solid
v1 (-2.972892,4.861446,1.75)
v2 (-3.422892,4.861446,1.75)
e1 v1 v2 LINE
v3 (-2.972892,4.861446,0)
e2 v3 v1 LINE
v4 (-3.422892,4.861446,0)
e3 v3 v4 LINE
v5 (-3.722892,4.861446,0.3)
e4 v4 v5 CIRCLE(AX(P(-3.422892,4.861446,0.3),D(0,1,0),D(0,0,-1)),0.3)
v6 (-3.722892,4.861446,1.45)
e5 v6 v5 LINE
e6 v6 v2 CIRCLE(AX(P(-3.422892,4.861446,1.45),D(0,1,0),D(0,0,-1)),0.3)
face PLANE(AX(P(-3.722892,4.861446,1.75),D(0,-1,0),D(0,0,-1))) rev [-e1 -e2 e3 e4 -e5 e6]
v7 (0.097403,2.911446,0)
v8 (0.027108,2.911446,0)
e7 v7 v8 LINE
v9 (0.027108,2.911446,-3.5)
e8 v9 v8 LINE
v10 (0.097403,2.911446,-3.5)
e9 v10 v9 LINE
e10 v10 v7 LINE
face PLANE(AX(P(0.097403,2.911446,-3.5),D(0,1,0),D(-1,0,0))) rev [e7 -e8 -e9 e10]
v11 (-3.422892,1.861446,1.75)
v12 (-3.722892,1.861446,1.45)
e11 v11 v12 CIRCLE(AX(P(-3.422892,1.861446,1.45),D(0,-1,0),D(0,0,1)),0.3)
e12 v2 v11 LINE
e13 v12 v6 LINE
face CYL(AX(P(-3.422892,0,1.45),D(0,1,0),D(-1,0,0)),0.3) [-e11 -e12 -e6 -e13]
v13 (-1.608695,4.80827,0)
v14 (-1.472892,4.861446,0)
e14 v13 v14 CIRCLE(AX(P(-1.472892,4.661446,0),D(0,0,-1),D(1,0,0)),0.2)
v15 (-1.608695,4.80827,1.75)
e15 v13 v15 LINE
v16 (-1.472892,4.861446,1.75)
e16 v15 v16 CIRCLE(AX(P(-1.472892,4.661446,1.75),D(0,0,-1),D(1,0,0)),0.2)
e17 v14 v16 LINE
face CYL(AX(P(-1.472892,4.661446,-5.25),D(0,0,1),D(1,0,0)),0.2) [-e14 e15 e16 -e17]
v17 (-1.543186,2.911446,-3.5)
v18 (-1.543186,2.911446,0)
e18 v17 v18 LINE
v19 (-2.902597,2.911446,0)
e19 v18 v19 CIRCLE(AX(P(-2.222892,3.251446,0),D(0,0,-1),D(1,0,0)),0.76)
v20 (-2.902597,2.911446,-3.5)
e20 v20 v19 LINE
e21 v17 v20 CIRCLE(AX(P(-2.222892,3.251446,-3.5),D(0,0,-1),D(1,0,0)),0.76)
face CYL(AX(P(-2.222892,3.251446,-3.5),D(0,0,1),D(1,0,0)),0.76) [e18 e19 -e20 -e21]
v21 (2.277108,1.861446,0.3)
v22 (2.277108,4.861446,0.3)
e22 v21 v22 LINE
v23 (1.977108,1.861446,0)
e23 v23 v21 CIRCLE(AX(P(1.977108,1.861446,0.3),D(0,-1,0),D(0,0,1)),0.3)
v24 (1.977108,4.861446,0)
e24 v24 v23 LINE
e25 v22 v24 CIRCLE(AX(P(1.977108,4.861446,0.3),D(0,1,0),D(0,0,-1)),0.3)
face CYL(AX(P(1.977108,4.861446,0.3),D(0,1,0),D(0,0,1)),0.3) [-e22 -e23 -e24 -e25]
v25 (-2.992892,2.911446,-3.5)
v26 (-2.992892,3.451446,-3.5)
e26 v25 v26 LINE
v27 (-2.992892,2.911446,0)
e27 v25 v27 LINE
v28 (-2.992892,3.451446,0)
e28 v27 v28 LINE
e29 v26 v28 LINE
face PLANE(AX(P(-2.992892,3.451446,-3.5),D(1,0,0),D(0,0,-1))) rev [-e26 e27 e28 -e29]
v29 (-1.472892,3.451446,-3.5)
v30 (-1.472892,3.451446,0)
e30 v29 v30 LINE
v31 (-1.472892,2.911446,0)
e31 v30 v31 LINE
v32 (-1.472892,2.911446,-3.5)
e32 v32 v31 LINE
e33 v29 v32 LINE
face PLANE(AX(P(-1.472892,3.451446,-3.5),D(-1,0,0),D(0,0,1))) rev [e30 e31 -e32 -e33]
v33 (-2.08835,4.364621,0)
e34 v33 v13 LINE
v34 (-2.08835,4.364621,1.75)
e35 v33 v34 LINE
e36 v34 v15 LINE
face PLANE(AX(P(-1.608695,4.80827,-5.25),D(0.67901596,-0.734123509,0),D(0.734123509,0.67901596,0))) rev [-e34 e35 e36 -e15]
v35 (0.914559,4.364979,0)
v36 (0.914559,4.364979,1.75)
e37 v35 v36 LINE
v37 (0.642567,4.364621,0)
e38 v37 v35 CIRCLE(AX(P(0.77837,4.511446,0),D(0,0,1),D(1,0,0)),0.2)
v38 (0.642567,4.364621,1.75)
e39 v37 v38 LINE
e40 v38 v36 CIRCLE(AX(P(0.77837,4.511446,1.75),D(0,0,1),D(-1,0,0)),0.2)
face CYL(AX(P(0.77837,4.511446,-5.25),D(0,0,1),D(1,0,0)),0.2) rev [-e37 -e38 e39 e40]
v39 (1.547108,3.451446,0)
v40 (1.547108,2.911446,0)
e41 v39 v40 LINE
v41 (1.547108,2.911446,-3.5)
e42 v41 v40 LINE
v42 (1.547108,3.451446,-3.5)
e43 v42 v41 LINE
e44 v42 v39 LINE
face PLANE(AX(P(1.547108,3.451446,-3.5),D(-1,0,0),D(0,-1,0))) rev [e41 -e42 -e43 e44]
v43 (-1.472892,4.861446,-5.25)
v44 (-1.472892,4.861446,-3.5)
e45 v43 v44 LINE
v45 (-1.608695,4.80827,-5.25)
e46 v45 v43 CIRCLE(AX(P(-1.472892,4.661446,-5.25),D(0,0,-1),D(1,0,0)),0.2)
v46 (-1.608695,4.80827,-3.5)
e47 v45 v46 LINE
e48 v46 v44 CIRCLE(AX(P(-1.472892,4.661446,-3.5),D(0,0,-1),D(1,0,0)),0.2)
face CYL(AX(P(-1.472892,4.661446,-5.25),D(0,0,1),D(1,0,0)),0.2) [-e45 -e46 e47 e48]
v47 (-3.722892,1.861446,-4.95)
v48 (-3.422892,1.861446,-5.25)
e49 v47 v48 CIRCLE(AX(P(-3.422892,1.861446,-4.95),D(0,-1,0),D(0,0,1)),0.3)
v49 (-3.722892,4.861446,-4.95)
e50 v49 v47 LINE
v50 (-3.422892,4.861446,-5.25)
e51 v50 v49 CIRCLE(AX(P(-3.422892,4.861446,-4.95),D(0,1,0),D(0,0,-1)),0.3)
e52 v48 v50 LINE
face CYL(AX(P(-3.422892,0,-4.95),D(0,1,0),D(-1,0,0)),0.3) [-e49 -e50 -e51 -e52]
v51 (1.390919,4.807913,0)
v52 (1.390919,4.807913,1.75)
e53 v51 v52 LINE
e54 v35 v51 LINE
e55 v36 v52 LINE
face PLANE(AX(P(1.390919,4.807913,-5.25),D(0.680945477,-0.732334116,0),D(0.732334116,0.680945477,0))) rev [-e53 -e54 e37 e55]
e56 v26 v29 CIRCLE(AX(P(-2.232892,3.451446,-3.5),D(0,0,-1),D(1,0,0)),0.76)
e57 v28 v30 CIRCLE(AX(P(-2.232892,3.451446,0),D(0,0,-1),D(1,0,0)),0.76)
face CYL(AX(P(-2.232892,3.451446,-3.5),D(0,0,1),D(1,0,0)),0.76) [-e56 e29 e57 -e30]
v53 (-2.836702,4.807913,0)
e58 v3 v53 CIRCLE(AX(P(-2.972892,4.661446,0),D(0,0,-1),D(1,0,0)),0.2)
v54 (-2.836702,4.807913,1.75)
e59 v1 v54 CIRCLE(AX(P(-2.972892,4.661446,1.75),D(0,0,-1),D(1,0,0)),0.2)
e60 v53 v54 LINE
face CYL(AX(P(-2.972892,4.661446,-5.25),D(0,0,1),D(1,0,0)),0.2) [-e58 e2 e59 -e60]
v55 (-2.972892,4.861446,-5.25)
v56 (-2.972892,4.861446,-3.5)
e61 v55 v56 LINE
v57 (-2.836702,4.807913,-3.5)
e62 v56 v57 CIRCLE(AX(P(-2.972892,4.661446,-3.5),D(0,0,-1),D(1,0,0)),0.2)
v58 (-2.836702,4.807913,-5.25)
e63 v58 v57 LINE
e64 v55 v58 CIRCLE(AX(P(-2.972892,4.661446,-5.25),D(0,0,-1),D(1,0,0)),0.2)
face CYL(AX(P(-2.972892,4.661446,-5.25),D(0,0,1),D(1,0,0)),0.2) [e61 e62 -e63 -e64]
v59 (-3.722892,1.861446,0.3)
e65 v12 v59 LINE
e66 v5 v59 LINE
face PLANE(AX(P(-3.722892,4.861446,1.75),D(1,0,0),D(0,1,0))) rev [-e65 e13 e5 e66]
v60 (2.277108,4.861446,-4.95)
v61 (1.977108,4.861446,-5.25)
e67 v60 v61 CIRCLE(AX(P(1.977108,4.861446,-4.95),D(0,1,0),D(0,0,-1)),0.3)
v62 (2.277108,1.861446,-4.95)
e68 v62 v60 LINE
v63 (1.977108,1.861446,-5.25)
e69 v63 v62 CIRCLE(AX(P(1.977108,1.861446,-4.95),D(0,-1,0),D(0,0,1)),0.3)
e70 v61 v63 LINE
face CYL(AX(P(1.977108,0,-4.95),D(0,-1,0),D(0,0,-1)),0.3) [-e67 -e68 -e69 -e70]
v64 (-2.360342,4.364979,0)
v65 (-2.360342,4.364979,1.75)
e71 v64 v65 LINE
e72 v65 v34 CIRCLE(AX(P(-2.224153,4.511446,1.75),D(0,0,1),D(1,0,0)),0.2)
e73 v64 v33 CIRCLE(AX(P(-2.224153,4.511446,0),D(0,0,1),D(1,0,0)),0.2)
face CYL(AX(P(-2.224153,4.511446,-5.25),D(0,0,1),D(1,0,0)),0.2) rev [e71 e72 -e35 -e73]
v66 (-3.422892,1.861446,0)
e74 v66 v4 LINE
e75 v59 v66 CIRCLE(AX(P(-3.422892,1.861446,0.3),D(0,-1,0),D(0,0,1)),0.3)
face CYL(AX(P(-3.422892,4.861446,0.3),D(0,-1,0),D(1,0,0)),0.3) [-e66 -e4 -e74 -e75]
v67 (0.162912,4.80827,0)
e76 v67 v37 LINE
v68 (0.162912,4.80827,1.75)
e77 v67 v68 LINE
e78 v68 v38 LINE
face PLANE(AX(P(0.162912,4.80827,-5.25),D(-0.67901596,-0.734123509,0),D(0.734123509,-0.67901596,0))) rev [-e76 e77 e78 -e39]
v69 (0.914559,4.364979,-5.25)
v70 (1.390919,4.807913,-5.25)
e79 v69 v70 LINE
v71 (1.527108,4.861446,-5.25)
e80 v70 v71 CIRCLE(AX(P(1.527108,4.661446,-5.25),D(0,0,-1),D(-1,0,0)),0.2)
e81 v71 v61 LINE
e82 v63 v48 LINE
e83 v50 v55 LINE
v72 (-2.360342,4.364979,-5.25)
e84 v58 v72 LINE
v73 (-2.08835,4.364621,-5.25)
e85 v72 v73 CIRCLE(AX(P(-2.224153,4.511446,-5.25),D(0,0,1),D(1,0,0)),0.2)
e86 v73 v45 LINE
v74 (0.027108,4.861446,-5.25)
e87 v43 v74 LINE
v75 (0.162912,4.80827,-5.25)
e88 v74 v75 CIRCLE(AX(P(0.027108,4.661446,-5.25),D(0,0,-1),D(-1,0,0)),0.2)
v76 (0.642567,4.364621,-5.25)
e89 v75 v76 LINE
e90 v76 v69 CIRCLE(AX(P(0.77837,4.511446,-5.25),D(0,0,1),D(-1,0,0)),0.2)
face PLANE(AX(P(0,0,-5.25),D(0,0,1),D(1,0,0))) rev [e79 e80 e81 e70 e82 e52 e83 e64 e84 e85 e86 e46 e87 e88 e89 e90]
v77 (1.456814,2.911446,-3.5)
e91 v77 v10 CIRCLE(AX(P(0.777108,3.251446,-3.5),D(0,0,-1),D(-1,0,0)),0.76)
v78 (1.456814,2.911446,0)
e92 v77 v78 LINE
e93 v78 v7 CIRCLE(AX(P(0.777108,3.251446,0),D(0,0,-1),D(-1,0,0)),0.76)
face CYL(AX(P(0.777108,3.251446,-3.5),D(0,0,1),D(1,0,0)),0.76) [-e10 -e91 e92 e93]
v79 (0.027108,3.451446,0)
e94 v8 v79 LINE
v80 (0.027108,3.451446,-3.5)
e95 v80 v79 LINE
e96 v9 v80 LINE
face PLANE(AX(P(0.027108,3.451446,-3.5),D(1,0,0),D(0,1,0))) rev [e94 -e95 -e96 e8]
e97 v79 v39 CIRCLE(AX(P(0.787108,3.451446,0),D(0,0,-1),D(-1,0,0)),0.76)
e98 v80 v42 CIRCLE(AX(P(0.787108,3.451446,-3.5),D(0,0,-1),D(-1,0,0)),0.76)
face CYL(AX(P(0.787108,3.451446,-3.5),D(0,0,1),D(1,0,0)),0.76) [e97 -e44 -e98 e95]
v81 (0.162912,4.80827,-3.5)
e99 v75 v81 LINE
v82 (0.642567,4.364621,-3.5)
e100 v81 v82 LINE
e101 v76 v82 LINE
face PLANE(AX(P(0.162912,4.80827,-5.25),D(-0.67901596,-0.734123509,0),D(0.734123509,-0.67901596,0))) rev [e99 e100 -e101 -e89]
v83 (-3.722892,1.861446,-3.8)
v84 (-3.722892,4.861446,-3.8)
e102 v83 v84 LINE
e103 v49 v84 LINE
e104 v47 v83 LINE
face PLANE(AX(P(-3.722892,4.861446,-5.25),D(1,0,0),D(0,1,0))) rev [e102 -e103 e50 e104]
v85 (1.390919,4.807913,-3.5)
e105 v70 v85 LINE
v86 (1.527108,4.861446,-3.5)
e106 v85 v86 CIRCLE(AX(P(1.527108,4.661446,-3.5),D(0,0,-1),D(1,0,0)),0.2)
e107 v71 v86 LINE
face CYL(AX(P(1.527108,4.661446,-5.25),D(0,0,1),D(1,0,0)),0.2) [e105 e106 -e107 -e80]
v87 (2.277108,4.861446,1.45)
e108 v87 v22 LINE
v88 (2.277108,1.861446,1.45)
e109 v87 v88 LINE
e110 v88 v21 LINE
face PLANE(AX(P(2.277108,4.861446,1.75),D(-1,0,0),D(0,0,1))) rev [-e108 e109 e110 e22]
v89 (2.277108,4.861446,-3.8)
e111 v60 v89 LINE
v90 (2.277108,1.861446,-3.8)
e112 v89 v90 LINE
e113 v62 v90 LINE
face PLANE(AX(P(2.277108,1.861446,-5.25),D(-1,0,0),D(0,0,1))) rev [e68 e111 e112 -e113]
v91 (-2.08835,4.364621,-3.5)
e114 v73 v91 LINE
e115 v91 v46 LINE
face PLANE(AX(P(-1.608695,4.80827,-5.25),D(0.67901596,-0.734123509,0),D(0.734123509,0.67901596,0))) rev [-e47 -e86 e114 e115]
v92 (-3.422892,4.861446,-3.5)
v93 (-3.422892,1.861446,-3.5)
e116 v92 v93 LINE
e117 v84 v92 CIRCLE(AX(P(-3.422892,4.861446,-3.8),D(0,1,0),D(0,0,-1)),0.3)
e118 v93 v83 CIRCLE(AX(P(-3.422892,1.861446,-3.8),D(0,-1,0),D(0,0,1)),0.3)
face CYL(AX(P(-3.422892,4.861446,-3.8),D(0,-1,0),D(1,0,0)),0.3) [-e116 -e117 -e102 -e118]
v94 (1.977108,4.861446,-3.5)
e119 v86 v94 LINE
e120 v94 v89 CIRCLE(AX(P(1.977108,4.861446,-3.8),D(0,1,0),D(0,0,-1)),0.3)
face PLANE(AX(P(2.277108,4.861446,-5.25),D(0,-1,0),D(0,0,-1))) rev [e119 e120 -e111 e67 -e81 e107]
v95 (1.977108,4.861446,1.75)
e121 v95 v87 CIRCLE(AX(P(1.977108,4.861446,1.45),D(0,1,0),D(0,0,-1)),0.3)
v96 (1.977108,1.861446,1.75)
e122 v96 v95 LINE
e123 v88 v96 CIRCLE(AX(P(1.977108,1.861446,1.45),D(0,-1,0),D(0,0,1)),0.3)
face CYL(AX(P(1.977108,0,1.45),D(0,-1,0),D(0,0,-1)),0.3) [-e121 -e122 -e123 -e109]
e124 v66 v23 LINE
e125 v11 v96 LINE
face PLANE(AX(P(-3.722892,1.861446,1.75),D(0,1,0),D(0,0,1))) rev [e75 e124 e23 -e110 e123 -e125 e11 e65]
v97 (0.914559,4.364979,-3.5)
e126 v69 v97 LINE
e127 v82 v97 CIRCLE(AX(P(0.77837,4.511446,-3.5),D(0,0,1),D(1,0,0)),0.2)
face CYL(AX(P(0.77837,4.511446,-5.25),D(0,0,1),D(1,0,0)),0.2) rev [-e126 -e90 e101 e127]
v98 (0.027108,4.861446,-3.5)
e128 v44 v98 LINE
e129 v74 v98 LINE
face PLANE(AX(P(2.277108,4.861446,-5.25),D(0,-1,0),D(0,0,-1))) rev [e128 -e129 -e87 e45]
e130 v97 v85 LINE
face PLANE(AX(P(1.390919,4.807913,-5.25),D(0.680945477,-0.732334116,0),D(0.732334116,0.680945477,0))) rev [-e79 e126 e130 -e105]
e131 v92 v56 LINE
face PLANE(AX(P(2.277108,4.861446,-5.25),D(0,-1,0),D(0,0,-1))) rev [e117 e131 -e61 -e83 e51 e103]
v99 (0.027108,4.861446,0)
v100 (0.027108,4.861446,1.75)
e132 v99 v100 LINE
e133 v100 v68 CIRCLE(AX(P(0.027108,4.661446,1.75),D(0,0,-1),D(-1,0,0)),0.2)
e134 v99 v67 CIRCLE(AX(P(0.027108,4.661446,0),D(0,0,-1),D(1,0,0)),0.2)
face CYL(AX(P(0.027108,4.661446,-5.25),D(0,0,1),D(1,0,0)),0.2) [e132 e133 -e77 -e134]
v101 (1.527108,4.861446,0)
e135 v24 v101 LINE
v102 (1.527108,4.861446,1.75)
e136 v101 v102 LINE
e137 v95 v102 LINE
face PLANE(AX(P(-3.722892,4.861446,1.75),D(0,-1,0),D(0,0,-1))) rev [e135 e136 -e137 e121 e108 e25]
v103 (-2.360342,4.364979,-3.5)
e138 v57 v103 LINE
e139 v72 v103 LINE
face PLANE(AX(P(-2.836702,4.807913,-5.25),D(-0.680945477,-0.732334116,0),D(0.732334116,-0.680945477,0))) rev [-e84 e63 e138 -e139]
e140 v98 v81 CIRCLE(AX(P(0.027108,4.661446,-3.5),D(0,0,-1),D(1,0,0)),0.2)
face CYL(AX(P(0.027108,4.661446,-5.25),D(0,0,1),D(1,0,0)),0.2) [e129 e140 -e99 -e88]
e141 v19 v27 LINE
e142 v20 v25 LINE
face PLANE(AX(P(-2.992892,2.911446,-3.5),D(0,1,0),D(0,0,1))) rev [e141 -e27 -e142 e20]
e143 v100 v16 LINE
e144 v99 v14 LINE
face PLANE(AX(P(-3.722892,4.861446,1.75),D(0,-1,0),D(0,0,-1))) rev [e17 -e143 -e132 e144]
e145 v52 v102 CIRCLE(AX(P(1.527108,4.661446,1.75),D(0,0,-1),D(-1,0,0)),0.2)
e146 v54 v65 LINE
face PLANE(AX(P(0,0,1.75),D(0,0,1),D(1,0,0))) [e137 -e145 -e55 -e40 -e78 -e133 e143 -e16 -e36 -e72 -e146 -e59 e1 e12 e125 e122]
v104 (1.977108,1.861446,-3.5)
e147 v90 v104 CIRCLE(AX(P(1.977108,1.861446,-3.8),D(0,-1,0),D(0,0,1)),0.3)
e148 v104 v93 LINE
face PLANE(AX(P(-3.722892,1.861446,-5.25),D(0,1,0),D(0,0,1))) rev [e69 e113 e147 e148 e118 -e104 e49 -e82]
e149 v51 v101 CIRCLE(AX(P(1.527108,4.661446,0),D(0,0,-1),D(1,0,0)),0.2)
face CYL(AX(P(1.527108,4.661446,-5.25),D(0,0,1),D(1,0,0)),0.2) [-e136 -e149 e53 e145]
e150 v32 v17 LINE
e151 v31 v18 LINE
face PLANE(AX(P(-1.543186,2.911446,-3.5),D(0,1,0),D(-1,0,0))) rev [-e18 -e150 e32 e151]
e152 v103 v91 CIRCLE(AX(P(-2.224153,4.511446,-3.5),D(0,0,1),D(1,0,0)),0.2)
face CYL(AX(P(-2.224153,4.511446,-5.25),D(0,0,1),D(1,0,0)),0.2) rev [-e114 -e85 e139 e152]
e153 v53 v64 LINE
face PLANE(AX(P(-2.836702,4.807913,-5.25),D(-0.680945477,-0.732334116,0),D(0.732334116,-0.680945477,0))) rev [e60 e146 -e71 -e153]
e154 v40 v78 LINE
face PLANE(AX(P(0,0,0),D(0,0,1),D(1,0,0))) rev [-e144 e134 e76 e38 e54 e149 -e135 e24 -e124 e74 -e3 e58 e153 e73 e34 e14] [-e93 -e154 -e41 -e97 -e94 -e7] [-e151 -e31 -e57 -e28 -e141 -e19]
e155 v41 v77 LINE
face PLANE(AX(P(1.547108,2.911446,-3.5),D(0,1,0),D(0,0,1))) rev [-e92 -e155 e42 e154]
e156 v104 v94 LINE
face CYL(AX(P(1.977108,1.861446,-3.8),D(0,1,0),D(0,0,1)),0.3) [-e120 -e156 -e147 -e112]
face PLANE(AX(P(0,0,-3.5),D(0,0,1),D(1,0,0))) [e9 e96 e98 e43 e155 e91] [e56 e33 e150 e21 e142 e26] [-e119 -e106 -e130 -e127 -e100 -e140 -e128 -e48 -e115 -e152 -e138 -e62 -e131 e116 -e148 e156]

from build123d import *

# Parameters (mm, degrees)
SKETCH_1_W          = 6
SKETCH_1_H          = 3
EXTRUDE_1_DEPTH     = 1.75
EXTRUDE_2_DEPTH     = 3.5
FILLET_5_R          = 0.3
FILLET_6_R          = 0.3
FILLET_7_R          = 0.3
FILLET_8_R          = 0.3
SKETCH_6_W          = 6
SKETCH_6_H          = 3
EXTRUDE_4_DEPTH     = 1.75
FILLET_9_R          = 0.3
FILLET_10_R         = 0.3
FILLET_11_R         = 0.3
FILLET_12_R         = 0.3
CUT_EXTRUDE_1_DEPTH = 10.300192295


with BuildPart() as part:
    # 草图1 → 凸台-拉伸1 (new body)
    with BuildSketch(Plane.XY):
        with Locations((-0.722891566, 3.361445783)):
            Rectangle(SKETCH_1_W, SKETCH_1_H)
    extrude(amount=EXTRUDE_1_DEPTH)

    # 草图2 → 凸台-拉伸2 (add)
    with BuildSketch(Plane(origin=(0, 0, 0), x_dir=(-1, 0, 0), z_dir=(0, 0, -1))):
        with BuildLine():
            Line((-0.097402615, 2.911445783), (-0.027108434, 2.911445783))
            Line((-0.027108434, 2.911445783), (-0.027108434, 3.451445783))
            ThreePointArc((-0.027108434, 3.451445783), (-0.787108434, 4.211445783), (-1.547108434, 3.451445783))
            Line((-1.547108434, 3.451445783), (-1.547108434, 2.911445783))
            Line((-1.547108434, 2.911445783), (-1.456814252, 2.911445783))
            ThreePointArc((-1.456814252, 2.911445783), (-0.777108434, 2.491445783), (-0.097402615, 2.911445783))
        make_face()
        with BuildLine():
            Line((1.472891566, 3.451445783), (1.472891566, 2.911445783))
            Line((1.472891566, 2.911445783), (1.543185748, 2.911445783))
            ThreePointArc((1.543185748, 2.911445783), (2.222891566, 2.491445783), (2.902597385, 2.911445783))
            Line((2.902597385, 2.911445783), (2.992891566, 2.911445783))
            Line((2.992891566, 2.911445783), (2.992891566, 3.451445783))
            ThreePointArc((2.992891566, 3.451445783), (2.232891566, 4.211445783), (1.472891566, 3.451445783))
        make_face()
    extrude(amount=EXTRUDE_2_DEPTH)

    # 圆角5
    fillet_5_edges = [part.edges().sort_by_distance(p)[0] for p in [
        (2.277108434, 3.361445783, 1.75),
    ]]
    fillet(fillet_5_edges, radius=FILLET_5_R)

    # 圆角6
    fillet_6_edges = [part.edges().sort_by_distance(p)[0] for p in [
        (2.277108434, 3.361445783, 0),
    ]]
    fillet(fillet_6_edges, radius=FILLET_6_R)

    # 圆角7
    fillet_7_edges = [part.edges().sort_by_distance(p)[0] for p in [
        (-3.722891566, 3.361445783, 1.75),
    ]]
    fillet(fillet_7_edges, radius=FILLET_7_R)

    # 圆角8
    fillet_8_edges = [part.edges().sort_by_distance(p)[0] for p in [
        (-3.722891566, 3.361445783, 0),
    ]]
    fillet(fillet_8_edges, radius=FILLET_8_R)

    # 草图6 → 凸台-拉伸4 (add)
    with BuildSketch(Plane(origin=(0, 0, -3.5), x_dir=(-1, 0, 0), z_dir=(0, 0, -1))):
        with Locations((0.722891566, 3.361445783)):
            Rectangle(SKETCH_6_W, SKETCH_6_H)
    extrude(amount=EXTRUDE_4_DEPTH)

    # 圆角9
    fillet_9_edges = [part.edges().sort_by_distance(p)[0] for p in [
        (2.277108434, 3.361445783, -5.25),
    ]]
    fillet(fillet_9_edges, radius=FILLET_9_R)

    # 圆角10
    fillet_10_edges = [part.edges().sort_by_distance(p)[0] for p in [
        (2.277108434, 3.361445783, -3.5),
    ]]
    fillet(fillet_10_edges, radius=FILLET_10_R)

    # 圆角11
    fillet_11_edges = [part.edges().sort_by_distance(p)[0] for p in [
        (-3.722891566, 3.361445783, -5.25),
    ]]
    fillet(fillet_11_edges, radius=FILLET_11_R)

    # 圆角12
    fillet_12_edges = [part.edges().sort_by_distance(p)[0] for p in [
        (-3.722891566, 3.361445783, -3.5),
    ]]
    fillet(fillet_12_edges, radius=FILLET_12_R)

    # 草图7 → 切除-拉伸1 (cut, through all)
    with BuildSketch(Plane.XY.offset(1.75)):
        with BuildLine():
            Line((-2.972891566, 4.861445783), (-1.472891566, 4.861445783))
            ThreePointArc((-1.472891566, 4.861445783), (-1.545812961, 4.847678085), (-1.608694758, 4.808270485))
            Line((-1.608694758, 4.808270485), (-2.088349842, 4.364621081))
            ThreePointArc((-2.088349842, 4.364621081), (-2.224416187, 4.311445956), (-2.360342129, 4.36497896))
            Line((-2.360342129, 4.36497896), (-2.836702471, 4.807912606))
            ThreePointArc((-2.836702471, 4.807912606), (-2.899725196, 4.847581976), (-2.972891566, 4.861445783))
        make_face()
        with BuildLine():
            Line((0.162911626, 4.808270485), (0.642566709, 4.364621081))
            ThreePointArc((0.642566709, 4.364621081), (0.778633055, 4.311445956), (0.914558997, 4.36497896))
            Line((0.914558997, 4.36497896), (1.390919338, 4.807912606))
            ThreePointArc((1.390919338, 4.807912606), (1.453942064, 4.847581976), (1.527108434, 4.861445783))
            Line((1.527108434, 4.861445783), (0.027108434, 4.861445783))
            ThreePointArc((0.027108434, 4.861445783), (0.100029829, 4.847678085), (0.162911626, 4.808270485))
        make_face()
    extrude(amount=-CUT_EXTRUDE_1_DEPTH, mode=Mode.SUBTRACT)


solid = part.part
